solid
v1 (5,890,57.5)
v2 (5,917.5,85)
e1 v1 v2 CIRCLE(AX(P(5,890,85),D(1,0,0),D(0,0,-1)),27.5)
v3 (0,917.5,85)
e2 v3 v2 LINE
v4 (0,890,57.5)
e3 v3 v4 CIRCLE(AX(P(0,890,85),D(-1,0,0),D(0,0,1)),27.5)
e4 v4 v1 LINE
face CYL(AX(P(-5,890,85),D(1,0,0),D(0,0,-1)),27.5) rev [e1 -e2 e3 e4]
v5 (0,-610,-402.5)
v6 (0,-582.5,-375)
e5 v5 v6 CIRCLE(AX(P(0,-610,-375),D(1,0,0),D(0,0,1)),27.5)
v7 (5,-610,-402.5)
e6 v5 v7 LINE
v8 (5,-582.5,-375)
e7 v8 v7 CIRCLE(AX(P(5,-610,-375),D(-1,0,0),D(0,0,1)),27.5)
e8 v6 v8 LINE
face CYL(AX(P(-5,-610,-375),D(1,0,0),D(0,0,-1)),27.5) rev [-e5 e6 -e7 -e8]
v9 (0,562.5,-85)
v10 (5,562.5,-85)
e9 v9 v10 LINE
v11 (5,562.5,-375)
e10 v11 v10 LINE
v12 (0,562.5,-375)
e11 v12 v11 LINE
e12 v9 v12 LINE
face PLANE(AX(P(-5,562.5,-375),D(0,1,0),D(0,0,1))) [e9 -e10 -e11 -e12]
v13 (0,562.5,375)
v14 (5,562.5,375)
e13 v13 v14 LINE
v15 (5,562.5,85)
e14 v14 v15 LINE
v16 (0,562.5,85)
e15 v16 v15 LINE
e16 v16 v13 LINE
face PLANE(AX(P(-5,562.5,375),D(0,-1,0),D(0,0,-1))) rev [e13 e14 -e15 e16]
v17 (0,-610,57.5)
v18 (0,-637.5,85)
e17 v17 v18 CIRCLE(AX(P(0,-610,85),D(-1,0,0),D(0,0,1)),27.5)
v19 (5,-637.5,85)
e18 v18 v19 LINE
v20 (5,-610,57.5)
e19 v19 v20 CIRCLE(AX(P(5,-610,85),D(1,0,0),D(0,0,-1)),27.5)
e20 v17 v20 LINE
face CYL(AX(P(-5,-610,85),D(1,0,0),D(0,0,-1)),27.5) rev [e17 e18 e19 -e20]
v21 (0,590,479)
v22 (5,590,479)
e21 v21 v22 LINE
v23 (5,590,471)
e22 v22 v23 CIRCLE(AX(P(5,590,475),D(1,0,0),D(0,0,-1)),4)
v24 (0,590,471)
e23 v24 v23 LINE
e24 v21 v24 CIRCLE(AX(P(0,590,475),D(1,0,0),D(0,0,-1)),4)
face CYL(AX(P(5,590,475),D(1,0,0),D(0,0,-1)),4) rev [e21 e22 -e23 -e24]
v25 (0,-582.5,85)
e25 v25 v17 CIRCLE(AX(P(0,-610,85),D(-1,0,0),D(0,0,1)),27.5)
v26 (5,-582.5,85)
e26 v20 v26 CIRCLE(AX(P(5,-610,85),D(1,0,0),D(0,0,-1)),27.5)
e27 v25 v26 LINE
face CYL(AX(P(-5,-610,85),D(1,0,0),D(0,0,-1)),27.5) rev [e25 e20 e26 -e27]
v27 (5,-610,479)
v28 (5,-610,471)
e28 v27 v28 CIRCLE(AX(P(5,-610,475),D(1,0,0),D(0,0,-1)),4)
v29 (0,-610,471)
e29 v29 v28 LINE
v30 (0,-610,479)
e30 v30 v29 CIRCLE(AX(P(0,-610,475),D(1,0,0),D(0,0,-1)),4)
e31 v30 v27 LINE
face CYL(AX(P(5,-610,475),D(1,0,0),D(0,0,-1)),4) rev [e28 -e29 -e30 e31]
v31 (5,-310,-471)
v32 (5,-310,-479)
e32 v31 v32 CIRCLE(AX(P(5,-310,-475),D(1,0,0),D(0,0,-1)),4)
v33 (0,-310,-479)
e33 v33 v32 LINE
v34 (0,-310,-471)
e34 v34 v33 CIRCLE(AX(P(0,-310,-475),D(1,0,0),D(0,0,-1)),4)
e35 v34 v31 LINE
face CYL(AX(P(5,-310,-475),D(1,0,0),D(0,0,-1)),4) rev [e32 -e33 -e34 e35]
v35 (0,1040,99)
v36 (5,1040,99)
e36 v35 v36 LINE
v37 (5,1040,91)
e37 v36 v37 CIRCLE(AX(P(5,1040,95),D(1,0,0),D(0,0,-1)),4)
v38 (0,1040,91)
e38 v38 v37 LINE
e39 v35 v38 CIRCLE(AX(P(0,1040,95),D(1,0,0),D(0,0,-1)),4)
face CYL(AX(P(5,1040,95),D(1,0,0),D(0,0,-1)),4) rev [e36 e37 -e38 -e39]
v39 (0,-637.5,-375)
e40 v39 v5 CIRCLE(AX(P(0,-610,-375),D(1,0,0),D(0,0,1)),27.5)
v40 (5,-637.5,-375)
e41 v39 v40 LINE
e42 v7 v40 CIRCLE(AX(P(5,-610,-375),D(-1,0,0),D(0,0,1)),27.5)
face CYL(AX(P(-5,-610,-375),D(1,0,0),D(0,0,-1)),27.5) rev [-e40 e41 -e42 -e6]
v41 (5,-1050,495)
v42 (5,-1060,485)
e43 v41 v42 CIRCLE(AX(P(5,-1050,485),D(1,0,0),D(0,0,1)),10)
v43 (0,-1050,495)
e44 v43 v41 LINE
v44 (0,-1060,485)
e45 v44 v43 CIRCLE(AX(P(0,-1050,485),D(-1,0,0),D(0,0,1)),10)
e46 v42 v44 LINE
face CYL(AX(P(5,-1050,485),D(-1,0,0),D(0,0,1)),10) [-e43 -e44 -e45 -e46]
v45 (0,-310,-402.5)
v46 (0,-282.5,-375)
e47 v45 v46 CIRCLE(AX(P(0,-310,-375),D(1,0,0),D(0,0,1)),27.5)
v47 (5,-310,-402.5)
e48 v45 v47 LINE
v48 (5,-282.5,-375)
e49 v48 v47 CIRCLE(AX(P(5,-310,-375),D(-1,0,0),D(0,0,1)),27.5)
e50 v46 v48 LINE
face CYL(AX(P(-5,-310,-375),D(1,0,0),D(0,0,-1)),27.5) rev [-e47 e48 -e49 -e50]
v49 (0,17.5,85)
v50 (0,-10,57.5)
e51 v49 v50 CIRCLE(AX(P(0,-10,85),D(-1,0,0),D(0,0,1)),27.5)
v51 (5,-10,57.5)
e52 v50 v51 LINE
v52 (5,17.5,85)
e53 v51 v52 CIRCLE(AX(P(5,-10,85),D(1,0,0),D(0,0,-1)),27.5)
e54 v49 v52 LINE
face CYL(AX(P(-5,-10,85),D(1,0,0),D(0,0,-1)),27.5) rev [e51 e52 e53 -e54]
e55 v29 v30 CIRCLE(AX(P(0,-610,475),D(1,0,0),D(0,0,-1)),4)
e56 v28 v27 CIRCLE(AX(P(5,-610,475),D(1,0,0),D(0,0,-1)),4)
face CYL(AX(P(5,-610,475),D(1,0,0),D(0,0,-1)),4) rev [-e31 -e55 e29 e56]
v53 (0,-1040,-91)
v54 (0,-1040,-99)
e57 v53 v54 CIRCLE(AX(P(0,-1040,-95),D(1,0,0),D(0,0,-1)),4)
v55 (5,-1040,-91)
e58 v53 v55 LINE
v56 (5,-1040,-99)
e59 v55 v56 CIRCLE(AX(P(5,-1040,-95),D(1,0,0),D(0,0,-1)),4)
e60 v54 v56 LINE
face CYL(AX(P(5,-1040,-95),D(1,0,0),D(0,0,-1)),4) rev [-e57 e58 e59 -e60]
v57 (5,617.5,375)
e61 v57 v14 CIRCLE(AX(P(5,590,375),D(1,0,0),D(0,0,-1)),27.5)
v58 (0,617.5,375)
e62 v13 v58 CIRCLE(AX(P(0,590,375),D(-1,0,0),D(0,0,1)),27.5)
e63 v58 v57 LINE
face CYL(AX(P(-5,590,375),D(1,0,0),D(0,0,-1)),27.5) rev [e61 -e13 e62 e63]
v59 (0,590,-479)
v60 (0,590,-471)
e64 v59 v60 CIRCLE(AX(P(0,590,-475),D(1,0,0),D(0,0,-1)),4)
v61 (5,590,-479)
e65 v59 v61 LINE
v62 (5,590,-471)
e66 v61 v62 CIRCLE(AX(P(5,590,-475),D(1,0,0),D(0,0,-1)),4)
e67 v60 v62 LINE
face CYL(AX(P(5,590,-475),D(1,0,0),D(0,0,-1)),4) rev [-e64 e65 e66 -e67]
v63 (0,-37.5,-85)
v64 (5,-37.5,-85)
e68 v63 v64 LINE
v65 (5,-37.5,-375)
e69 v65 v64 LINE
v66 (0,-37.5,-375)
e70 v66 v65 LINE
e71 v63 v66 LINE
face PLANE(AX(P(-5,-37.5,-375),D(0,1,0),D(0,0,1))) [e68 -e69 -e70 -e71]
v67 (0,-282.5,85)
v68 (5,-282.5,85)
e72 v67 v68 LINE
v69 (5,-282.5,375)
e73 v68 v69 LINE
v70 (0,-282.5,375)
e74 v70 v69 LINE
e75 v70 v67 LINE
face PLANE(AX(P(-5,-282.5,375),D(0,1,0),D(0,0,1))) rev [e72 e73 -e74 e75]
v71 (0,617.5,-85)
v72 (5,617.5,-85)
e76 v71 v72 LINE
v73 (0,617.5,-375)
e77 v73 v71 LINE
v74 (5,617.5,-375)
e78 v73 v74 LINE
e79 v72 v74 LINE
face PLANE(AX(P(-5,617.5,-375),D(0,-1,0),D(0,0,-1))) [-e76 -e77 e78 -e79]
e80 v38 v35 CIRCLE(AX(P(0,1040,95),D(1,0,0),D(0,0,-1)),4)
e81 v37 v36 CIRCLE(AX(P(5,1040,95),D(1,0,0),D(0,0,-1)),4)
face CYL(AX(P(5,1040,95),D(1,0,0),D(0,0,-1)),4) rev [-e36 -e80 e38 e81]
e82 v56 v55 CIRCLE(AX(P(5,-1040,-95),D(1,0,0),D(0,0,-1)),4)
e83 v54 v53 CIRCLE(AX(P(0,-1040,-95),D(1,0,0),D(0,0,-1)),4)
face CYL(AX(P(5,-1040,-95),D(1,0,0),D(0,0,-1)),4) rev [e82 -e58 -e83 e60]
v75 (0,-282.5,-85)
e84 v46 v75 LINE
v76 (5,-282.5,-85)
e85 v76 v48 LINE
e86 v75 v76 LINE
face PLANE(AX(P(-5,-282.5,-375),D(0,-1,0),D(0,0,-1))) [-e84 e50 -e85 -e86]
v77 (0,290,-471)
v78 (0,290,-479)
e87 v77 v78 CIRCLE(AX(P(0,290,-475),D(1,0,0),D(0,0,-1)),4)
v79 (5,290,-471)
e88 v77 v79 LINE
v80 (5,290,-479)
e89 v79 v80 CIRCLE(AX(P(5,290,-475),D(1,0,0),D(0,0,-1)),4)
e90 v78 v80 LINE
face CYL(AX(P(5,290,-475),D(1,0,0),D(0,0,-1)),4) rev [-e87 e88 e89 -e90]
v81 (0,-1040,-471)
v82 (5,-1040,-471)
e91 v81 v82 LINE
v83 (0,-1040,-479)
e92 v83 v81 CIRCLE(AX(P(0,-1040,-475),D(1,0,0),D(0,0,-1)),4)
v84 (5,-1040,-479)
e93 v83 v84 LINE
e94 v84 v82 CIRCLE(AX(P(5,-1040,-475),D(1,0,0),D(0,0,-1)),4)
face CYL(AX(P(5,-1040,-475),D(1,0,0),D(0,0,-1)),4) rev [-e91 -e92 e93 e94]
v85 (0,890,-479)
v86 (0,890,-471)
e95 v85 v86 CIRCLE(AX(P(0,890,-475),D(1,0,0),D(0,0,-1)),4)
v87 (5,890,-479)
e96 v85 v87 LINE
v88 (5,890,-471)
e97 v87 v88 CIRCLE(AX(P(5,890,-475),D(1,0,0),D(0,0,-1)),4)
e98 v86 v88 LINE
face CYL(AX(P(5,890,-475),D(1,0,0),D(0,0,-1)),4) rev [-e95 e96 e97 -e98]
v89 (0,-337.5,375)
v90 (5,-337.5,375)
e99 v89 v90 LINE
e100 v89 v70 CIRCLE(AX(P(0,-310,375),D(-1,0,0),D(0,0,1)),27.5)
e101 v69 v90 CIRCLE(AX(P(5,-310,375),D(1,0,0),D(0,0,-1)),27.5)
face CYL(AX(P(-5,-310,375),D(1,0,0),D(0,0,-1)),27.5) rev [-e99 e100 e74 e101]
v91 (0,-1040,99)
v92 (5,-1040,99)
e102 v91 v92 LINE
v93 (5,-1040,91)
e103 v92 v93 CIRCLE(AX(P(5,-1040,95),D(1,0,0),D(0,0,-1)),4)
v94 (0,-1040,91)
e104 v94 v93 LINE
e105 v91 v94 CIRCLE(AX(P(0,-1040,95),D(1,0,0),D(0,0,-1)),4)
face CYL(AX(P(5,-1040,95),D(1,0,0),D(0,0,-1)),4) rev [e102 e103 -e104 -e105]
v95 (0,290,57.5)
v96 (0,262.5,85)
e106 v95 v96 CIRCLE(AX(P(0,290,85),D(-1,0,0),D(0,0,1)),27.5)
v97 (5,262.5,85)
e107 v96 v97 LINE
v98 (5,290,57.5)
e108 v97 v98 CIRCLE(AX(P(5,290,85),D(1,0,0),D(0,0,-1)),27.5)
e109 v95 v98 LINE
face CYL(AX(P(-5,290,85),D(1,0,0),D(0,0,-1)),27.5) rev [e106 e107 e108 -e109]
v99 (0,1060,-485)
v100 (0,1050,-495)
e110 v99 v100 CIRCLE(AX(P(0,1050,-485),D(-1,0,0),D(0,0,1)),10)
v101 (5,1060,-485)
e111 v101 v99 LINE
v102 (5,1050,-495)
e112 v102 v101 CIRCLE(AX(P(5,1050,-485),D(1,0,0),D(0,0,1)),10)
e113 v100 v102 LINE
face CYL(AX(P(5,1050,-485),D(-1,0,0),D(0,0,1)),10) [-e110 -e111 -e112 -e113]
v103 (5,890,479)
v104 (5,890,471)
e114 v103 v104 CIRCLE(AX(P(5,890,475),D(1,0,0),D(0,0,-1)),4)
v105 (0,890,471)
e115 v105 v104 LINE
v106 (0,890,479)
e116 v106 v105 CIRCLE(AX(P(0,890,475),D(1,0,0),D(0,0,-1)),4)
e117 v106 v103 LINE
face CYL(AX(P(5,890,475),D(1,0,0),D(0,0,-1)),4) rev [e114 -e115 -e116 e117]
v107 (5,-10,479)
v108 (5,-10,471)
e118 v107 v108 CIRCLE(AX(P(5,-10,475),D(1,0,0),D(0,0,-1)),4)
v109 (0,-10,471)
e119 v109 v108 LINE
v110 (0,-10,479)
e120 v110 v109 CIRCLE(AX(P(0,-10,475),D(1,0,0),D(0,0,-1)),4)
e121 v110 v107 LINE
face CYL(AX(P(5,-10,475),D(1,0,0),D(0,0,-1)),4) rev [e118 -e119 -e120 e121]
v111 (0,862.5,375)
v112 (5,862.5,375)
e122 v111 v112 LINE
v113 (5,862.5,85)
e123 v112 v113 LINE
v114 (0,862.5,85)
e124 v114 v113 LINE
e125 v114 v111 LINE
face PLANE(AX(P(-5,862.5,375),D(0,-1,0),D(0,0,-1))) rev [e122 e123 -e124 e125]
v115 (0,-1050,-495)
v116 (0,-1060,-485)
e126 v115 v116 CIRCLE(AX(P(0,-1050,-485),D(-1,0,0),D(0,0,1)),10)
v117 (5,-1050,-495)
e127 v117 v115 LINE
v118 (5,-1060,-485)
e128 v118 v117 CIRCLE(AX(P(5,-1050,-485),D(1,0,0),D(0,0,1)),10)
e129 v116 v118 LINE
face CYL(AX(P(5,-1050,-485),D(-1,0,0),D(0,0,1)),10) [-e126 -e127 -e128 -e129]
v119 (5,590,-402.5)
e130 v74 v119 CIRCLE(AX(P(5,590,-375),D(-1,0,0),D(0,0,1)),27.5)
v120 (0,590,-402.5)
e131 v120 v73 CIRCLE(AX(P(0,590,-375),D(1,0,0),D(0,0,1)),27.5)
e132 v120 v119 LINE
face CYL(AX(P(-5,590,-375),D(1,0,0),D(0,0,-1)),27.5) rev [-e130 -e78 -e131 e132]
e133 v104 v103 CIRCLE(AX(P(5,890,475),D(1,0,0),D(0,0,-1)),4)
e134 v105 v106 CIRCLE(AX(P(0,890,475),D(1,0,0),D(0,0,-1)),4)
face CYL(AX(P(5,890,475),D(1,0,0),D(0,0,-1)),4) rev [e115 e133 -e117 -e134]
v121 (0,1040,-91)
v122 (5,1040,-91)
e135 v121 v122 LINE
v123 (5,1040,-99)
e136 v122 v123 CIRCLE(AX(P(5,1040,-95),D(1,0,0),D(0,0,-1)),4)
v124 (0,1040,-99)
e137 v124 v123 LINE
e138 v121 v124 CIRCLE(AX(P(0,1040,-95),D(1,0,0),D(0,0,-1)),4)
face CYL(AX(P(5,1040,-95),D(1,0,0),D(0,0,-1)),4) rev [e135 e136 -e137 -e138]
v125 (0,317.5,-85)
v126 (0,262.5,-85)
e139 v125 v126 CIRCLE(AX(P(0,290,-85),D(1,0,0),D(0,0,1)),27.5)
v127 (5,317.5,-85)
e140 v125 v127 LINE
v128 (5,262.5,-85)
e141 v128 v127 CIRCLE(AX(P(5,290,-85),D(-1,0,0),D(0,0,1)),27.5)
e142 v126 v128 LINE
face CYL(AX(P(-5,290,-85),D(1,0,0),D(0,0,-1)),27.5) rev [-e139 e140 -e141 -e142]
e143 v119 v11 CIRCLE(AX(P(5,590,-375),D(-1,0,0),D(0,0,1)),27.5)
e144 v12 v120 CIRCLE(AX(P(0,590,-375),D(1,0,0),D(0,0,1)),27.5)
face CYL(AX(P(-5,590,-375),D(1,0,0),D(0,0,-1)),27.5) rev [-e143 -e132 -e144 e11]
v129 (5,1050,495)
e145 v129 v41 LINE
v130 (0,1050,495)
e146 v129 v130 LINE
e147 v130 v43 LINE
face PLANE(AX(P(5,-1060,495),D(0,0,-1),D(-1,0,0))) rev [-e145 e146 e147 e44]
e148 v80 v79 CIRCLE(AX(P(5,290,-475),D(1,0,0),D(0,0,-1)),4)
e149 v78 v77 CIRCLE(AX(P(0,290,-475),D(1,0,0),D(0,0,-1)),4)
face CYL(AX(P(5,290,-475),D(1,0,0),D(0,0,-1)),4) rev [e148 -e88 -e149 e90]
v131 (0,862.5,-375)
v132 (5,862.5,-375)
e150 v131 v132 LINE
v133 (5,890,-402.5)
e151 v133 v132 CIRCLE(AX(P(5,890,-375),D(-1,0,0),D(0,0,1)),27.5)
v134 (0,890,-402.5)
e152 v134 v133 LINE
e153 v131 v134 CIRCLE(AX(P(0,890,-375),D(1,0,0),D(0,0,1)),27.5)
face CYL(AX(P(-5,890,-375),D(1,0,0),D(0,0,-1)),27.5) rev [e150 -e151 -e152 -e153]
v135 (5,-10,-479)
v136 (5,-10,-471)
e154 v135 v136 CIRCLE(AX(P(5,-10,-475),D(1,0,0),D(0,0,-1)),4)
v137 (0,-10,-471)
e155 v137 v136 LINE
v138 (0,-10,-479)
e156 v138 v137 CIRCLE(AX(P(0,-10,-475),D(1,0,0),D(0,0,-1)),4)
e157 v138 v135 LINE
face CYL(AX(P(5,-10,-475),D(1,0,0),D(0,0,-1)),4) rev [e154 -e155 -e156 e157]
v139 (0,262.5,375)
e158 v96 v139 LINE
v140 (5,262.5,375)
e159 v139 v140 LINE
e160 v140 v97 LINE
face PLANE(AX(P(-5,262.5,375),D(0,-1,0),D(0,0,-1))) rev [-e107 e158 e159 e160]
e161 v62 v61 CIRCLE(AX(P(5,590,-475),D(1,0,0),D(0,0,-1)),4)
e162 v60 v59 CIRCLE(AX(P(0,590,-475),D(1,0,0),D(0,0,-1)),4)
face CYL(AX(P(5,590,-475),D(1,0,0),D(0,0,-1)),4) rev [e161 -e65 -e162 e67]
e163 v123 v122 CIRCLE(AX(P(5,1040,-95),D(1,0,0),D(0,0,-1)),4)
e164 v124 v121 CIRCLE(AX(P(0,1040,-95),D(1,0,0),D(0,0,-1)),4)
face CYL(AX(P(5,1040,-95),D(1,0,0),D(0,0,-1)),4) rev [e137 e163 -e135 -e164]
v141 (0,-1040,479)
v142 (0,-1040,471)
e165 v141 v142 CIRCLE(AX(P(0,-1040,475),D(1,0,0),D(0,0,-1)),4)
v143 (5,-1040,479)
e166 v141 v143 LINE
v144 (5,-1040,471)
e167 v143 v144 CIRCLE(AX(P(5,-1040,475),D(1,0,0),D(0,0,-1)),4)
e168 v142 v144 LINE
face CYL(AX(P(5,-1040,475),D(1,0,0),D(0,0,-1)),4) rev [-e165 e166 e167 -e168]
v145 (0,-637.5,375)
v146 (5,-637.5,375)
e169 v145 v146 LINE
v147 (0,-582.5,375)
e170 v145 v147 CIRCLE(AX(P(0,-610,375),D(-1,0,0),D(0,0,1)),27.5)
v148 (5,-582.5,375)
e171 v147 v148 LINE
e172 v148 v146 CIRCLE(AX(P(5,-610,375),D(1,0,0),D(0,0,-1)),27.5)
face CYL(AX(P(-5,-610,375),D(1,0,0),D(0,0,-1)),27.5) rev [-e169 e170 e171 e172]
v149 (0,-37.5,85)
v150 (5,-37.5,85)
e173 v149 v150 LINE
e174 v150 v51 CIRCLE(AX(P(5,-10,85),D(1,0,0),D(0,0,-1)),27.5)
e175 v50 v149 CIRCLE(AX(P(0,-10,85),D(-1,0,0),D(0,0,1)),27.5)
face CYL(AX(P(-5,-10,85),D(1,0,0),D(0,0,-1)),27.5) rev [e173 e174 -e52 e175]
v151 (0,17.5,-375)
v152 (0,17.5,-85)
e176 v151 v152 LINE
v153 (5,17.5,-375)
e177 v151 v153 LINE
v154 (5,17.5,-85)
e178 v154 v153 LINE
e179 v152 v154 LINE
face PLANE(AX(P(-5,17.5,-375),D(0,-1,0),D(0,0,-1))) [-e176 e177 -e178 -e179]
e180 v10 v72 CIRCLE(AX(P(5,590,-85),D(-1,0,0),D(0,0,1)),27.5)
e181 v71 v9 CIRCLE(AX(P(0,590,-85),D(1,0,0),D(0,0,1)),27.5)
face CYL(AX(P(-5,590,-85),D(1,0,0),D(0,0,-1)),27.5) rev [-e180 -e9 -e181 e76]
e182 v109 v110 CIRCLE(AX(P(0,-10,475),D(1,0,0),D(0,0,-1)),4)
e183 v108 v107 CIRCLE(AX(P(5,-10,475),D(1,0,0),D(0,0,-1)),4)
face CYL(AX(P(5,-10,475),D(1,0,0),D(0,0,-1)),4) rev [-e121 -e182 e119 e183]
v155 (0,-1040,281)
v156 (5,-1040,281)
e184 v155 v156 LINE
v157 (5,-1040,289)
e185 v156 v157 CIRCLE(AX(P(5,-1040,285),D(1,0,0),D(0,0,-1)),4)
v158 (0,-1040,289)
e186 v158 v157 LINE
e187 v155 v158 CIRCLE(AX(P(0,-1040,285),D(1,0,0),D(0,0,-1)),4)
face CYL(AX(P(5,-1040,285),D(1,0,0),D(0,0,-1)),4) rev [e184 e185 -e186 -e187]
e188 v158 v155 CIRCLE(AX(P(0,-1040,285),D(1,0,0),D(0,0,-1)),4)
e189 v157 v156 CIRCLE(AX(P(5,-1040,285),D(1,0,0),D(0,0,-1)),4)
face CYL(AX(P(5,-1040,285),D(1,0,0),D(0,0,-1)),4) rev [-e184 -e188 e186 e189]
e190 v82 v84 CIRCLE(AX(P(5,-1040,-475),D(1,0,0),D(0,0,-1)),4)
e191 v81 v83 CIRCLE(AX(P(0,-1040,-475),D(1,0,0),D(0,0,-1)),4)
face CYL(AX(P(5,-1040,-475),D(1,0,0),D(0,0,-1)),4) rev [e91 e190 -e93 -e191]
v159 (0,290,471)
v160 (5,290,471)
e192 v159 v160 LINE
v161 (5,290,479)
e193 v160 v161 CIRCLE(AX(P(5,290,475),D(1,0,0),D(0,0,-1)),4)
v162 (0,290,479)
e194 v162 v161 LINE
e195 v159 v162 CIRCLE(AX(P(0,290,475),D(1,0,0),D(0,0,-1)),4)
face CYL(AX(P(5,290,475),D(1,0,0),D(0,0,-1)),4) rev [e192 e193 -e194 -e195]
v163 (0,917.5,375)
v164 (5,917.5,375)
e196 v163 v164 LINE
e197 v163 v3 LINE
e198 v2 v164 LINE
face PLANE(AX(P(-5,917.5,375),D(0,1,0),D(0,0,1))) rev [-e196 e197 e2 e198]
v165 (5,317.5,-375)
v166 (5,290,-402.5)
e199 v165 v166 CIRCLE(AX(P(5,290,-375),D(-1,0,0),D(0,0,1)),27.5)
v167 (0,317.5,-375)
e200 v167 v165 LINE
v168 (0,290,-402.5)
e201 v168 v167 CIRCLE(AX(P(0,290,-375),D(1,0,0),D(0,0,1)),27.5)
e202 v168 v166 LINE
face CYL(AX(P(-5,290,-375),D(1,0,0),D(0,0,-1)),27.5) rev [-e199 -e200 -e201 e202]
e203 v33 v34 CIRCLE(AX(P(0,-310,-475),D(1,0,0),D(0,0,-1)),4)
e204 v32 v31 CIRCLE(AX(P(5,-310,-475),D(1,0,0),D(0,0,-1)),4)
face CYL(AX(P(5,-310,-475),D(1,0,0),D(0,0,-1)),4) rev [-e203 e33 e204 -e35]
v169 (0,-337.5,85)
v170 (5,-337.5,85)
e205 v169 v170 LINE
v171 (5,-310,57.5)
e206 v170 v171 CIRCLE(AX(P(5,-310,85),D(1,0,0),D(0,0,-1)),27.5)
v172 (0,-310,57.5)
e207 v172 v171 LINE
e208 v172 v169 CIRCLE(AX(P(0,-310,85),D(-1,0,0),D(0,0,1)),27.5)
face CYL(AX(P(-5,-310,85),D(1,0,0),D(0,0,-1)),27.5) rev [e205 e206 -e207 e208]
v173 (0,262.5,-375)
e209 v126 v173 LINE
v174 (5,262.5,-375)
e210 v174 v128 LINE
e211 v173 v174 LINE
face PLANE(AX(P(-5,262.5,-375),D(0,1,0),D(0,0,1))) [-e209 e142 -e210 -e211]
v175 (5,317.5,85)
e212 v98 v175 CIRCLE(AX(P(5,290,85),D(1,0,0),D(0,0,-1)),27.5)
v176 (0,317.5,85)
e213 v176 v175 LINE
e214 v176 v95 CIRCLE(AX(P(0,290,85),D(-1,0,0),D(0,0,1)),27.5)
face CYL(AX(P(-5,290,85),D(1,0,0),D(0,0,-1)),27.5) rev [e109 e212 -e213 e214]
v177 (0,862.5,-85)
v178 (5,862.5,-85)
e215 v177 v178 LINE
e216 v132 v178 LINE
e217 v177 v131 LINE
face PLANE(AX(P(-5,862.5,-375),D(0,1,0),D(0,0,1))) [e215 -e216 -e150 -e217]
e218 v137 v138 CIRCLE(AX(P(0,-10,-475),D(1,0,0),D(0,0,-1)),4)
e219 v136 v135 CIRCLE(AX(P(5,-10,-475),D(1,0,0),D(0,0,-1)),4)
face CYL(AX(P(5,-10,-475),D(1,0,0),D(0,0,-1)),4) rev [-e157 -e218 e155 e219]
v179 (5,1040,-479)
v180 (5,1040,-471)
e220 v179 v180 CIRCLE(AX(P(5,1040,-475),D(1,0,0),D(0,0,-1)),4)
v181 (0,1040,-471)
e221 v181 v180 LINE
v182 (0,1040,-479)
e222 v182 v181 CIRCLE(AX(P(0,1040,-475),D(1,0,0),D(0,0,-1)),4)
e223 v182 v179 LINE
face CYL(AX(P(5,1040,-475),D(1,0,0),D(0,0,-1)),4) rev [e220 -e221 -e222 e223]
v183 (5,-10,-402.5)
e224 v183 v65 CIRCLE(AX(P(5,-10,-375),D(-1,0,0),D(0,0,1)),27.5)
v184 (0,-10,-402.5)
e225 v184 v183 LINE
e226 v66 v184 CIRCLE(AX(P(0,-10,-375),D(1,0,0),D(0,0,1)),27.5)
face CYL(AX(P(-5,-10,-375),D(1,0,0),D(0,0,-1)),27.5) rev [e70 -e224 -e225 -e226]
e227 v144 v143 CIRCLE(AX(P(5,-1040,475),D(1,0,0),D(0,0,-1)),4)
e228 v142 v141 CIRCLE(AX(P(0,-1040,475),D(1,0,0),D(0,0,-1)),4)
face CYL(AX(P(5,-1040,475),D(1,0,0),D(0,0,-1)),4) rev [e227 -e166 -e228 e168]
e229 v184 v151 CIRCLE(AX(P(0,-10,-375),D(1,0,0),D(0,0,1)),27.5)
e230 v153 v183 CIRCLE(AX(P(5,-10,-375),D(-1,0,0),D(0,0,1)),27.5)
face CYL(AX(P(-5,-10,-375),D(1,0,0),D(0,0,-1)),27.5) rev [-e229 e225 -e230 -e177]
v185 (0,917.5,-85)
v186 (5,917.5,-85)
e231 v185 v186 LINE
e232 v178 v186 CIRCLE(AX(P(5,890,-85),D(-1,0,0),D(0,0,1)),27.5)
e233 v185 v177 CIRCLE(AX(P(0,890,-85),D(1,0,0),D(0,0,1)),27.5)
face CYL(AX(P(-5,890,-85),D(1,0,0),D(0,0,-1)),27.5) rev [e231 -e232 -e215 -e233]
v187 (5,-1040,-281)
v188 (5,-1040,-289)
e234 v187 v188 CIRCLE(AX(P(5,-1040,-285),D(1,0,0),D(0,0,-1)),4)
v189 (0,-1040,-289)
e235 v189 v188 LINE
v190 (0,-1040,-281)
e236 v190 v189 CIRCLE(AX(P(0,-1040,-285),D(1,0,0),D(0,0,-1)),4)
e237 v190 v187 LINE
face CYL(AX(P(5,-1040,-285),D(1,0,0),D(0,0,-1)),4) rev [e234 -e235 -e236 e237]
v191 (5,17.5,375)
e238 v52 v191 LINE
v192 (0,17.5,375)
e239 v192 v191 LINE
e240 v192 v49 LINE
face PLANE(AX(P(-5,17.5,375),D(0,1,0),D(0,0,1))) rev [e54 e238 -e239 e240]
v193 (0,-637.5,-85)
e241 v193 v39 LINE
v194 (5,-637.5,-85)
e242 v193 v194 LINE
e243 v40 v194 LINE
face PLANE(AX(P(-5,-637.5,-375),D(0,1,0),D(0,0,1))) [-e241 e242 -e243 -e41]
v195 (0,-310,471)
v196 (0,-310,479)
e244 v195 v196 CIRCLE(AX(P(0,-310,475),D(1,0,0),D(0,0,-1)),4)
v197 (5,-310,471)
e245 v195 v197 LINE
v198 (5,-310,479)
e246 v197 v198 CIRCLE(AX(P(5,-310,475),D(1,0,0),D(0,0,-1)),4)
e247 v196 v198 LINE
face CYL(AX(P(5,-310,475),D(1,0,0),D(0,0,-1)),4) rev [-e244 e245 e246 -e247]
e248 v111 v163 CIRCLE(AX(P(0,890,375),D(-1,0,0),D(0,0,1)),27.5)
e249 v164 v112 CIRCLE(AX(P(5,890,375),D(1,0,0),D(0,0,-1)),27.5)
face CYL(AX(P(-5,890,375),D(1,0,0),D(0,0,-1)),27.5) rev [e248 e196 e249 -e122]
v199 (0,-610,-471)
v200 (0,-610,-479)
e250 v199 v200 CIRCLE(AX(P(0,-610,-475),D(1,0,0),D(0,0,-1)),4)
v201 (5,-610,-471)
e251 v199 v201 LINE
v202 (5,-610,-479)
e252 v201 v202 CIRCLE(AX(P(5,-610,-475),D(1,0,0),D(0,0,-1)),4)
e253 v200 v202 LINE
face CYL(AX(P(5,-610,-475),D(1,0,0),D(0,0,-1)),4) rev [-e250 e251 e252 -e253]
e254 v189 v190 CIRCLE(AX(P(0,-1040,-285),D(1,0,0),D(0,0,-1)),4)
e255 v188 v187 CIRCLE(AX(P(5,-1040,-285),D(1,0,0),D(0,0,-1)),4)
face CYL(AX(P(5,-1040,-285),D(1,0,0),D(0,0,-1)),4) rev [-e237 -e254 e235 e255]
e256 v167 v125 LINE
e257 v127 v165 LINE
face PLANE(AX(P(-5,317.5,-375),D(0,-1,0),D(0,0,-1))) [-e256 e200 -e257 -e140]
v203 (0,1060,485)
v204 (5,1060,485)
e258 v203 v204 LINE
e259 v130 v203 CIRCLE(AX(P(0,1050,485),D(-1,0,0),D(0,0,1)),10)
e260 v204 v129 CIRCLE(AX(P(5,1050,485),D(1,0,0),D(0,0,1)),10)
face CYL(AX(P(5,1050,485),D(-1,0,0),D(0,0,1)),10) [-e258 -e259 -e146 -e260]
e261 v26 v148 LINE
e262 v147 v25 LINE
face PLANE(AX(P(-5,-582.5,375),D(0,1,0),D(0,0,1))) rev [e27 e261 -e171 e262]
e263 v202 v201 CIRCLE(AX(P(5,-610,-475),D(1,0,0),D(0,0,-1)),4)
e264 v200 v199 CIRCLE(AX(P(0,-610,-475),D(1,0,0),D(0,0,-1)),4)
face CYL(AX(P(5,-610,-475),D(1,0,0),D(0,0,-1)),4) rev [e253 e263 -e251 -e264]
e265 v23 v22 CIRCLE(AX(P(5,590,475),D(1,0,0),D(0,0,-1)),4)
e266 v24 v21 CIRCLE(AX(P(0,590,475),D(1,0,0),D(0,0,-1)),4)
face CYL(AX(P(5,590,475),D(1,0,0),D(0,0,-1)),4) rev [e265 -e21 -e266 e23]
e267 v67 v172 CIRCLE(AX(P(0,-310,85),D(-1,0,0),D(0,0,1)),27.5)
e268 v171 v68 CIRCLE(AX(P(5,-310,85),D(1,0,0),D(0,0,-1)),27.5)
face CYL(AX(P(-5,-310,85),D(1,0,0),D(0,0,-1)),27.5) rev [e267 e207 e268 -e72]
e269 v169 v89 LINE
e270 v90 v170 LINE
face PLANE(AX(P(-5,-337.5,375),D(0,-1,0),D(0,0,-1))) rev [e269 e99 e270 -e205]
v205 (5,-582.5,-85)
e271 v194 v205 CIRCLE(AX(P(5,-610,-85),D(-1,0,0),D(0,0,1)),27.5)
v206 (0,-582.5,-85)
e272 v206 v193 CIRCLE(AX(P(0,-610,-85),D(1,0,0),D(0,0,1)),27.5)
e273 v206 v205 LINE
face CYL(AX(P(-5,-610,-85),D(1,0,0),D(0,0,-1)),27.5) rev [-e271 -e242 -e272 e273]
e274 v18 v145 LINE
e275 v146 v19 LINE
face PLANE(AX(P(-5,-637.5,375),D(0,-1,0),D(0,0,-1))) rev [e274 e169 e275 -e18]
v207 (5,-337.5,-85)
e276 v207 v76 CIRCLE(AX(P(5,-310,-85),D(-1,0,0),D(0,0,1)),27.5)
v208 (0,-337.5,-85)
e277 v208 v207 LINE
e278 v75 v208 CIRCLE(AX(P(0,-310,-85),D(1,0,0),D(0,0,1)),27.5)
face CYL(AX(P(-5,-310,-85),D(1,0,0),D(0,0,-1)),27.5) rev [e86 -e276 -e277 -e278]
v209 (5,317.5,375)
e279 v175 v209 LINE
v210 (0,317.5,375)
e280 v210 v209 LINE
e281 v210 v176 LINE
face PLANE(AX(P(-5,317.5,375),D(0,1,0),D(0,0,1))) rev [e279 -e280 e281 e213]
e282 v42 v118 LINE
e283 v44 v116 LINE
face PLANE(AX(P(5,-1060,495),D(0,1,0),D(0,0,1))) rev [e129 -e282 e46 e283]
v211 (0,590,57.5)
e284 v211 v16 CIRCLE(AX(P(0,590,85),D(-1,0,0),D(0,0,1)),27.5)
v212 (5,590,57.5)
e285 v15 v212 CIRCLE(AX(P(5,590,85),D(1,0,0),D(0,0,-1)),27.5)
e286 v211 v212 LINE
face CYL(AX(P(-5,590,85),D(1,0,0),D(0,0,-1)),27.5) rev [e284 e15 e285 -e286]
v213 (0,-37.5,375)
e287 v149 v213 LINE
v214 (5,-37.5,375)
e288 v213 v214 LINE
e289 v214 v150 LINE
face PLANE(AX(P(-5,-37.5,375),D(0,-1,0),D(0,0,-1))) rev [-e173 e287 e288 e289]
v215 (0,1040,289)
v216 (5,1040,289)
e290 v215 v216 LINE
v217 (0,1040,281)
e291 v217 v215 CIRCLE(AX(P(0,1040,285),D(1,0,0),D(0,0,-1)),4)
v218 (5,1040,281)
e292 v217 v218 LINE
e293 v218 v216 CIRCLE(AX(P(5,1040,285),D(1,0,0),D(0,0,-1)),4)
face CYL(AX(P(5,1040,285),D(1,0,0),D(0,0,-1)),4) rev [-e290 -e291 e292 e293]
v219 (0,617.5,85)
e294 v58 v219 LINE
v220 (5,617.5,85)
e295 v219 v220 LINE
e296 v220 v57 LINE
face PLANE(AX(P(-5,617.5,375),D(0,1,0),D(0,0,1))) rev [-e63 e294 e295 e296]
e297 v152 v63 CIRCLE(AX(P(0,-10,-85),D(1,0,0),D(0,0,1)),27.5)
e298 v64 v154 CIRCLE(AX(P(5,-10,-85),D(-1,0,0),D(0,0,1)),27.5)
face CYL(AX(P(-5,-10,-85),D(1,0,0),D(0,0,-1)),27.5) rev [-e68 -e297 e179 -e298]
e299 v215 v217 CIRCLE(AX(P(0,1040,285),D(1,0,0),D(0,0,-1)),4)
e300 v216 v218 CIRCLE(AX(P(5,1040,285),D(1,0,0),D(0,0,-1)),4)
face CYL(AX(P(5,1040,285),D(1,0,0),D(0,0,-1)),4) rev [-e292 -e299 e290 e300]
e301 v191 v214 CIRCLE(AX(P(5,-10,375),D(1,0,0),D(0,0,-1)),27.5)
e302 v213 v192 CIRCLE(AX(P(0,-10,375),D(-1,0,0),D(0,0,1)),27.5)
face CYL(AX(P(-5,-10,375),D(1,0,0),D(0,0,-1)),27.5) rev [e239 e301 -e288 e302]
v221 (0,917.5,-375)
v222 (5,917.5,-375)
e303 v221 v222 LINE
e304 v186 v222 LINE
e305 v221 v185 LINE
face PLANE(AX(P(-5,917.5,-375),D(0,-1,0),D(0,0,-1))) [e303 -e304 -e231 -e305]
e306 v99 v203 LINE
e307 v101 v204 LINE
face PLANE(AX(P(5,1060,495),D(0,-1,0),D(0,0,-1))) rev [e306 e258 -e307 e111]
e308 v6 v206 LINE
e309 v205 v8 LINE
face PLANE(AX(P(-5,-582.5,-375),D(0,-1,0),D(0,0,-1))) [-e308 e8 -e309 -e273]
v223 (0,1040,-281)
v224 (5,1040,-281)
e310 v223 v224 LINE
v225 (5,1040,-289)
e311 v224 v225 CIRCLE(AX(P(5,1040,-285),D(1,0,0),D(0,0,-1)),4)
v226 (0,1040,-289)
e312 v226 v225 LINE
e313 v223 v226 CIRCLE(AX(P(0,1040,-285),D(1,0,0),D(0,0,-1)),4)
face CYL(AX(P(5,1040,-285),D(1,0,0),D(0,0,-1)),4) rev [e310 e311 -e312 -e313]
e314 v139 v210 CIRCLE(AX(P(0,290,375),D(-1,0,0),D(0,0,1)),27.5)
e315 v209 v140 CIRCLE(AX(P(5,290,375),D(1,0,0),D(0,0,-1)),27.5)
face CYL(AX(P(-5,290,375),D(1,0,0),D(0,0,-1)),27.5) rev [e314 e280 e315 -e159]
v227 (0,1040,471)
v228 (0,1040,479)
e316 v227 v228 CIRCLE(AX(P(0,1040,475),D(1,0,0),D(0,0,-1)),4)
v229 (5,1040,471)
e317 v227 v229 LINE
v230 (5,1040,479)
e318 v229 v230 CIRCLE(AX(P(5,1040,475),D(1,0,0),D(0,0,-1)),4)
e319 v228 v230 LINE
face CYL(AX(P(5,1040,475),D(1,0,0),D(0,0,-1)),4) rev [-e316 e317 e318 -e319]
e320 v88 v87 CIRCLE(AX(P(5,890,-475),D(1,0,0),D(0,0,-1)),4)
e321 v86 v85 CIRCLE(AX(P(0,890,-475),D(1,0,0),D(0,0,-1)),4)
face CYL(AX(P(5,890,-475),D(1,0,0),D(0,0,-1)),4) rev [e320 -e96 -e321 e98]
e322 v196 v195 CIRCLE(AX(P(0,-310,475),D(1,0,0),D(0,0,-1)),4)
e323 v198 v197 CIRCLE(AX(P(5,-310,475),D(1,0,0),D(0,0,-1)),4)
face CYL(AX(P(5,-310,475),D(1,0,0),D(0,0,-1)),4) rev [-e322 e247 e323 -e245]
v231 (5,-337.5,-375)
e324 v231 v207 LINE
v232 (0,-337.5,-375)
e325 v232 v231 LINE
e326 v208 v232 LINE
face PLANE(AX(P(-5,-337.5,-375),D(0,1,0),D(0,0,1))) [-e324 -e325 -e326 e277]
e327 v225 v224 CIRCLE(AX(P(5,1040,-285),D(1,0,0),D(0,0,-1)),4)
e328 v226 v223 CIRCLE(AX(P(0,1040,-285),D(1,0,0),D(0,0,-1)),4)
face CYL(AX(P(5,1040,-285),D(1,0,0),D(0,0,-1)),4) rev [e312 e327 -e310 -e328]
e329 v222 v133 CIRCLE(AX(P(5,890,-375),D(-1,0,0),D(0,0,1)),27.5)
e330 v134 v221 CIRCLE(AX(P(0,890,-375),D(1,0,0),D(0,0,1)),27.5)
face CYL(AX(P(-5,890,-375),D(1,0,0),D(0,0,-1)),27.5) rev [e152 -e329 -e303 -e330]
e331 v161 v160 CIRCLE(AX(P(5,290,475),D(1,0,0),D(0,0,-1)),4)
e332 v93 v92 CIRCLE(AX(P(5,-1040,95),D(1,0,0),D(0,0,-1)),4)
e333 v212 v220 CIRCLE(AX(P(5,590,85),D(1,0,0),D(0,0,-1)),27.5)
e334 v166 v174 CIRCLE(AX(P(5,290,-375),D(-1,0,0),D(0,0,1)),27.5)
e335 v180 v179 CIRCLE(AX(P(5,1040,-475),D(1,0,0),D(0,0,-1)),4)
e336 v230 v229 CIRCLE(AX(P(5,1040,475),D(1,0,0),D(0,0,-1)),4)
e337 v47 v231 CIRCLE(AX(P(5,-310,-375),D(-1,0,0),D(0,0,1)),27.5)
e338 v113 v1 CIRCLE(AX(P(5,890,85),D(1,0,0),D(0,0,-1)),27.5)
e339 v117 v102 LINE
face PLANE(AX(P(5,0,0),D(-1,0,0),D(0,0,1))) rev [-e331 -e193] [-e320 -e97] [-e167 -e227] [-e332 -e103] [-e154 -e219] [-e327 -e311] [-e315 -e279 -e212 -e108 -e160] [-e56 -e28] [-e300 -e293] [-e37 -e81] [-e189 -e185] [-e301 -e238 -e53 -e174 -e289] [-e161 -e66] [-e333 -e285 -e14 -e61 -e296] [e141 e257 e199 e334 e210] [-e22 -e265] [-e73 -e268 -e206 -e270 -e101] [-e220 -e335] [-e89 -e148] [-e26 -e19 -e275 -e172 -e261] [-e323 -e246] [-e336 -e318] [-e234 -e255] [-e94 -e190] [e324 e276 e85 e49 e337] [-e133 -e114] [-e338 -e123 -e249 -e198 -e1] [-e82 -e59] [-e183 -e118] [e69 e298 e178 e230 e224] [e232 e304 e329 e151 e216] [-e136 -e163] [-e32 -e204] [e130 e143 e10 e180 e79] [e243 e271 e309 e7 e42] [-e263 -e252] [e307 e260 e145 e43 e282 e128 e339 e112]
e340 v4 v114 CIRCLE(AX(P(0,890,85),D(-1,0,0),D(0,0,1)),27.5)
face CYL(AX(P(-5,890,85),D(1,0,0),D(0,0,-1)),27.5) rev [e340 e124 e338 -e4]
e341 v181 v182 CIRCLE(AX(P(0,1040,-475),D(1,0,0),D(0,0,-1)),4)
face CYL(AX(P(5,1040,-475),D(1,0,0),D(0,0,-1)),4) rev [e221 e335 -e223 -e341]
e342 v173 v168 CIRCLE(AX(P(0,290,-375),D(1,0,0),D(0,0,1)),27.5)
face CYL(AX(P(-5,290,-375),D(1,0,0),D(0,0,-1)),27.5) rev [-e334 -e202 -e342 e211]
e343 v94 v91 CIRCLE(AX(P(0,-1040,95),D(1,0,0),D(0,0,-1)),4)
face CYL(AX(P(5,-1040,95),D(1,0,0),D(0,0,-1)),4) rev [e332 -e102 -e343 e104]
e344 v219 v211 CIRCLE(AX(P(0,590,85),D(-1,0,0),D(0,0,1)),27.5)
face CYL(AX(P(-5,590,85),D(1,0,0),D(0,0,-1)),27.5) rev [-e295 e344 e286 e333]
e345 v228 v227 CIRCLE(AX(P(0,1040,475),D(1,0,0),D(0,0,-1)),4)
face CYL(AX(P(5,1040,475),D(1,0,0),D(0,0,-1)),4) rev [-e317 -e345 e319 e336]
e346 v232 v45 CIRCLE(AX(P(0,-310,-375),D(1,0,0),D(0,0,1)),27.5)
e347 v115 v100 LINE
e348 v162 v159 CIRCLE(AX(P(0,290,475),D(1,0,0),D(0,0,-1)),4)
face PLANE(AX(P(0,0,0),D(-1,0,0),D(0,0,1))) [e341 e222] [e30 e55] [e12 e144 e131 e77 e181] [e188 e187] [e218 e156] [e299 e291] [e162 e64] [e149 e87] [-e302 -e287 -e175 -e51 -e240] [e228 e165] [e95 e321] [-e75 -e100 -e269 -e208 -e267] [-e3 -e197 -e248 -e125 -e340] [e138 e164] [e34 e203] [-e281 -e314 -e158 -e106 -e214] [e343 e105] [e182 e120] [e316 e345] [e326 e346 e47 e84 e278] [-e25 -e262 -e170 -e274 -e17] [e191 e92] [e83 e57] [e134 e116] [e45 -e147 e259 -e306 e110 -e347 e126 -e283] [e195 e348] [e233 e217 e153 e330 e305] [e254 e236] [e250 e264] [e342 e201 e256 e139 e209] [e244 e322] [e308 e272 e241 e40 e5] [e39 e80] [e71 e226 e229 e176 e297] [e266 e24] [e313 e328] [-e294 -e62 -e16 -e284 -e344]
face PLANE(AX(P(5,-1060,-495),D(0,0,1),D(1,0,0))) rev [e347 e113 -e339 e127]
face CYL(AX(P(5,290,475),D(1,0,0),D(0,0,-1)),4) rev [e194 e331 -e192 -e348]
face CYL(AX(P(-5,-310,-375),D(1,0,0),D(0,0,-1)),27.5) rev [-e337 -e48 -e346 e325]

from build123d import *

# Parameters (mm, degrees)
SKETCH1_W                     = 990
SKETCH1_H                     = 2120
BOSS_EXTRUDE1_DEPTH           = 5
FILLET1_R                     = 10
M7_CLEARANCE_HOLE3_D          = 8
M7_CLEARANCE_HOLE2_AT_2_COUNT = 2
M7_CLEARANCE_HOLE2_AT_2_PITCH = 950
LPATTERN7_COUNT               = 6
LPATTERN7_PITCH               = 300
CUT_EXTRUDE5_DEPTH            = 10
LPATTERN8_COUNT               = 6
LPATTERN8_PITCH               = 300
MIRROR6_COPY_1_DEPTH          = 10
MIRROR6_COPY_2_DEPTH          = 10
MIRROR6_COPY_3_DEPTH          = 10
MIRROR6_COPY_4_DEPTH          = 10
MIRROR6_COPY_5_DEPTH          = 10


with BuildPart() as part:
    # Sketch1 → Boss-Extrude1 (new body)
    with BuildSketch(Plane(origin=(0, 0, 0), x_dir=(0, 0, -1), z_dir=(1, 0, 0))):
        Rectangle(SKETCH1_W, SKETCH1_H)
    extrude(amount=BOSS_EXTRUDE1_DEPTH)

    # Fillet1
    fillet1_edges = [part.edges().sort_by_distance(p)[0] for p in [
        (2.5, -1060, -495),
        (2.5, -1060, 495),
        (2.5, 1060, 495),
        (2.5, 1060, -495),
    ]]
    fillet(fillet1_edges, radius=FILLET1_R)

    # M7 Clearance Hole3 (through all)
    with Locations(Plane(origin=(5, 0, 0), x_dir=(0, 0, -1), z_dir=(1, 0, 0))):
        with Locations((-475, 1040), (-285, 1040), (-95, 1040), (95, 1040), (285, 1040), (475, 1040)):
            m7_clearance_hole3 = Hole(M7_CLEARANCE_HOLE3_D / 2)

    # Mirror5: M7 Clearance Hole3 across plane
    add(m7_clearance_hole3.mirror(Plane(origin=(0, 0, 0), x_dir=(0, 0, 1), z_dir=(0, -1, 0))), mode=Mode.SUBTRACT)

    # Sketch15 → M7 Clearance Hole2 (revolve, cut)
    with BuildSketch(Plane(origin=(5, 890, 475), x_dir=(0, 0, -1), z_dir=(0, 1, 0))):
        Polygon((0, 0), (0, 7.403442476), (4, 5), (4, 0), align=None)
    m7_clearance_hole2 = revolve(axis=Axis((11.35, 890, 475), (-1, 0, 0)), mode=Mode.SUBTRACT)

    # M7 Clearance Hole2 at 2: M7 Clearance Hole2 ×2
    with Locations(*[(0, 0, -i * M7_CLEARANCE_HOLE2_AT_2_PITCH) for i in range(1, M7_CLEARANCE_HOLE2_AT_2_COUNT)]):
        add(m7_clearance_hole2, mode=Mode.SUBTRACT)

    # LPattern7: M7 Clearance Hole2 ×6
    with Locations(*[(0, -i * LPATTERN7_PITCH, 0) for i in range(1, LPATTERN7_COUNT)]):
        add(m7_clearance_hole2, mode=Mode.SUBTRACT)

    # LPattern7 copy 1 sketch → LPattern7 copy 1 (revolve, cut)
    with BuildSketch(Plane(origin=(5, 590, -475), x_dir=(0, 0, -1), z_dir=(0, 1, 0))):
        Polygon((0, 0), (0, 7.403442476), (4, 5), (4, 0), align=None)
    revolve(axis=Axis((11.35, 590, -475), (-1, 0, 0)), mode=Mode.SUBTRACT)

    # LPattern7 copy 2 sketch → LPattern7 copy 2 (revolve, cut)
    with BuildSketch(Plane(origin=(5, 290, -475), x_dir=(0, 0, -1), z_dir=(0, 1, 0))):
        Polygon((0, 0), (0, 7.403442476), (4, 5), (4, 0), align=None)
    revolve(axis=Axis((11.35, 290, -475), (-1, 0, 0)), mode=Mode.SUBTRACT)

    # LPattern7 copy 3 sketch → LPattern7 copy 3 (revolve, cut)
    with BuildSketch(Plane(origin=(5, -10, -475), x_dir=(0, 0, -1), z_dir=(0, 1, 0))):
        Polygon((0, 0), (0, 7.403442476), (4, 5), (4, 0), align=None)
    revolve(axis=Axis((11.35, -10, -475), (-1, 0, 0)), mode=Mode.SUBTRACT)

    # LPattern7 copy 4 sketch → LPattern7 copy 4 (revolve, cut)
    with BuildSketch(Plane(origin=(5, -310, -475), x_dir=(0, 0, -1), z_dir=(0, 1, 0))):
        Polygon((0, 0), (0, 7.403442476), (4, 5), (4, 0), align=None)
    revolve(axis=Axis((11.35, -310, -475), (-1, 0, 0)), mode=Mode.SUBTRACT)

    # LPattern7 copy 5 sketch → LPattern7 copy 5 (revolve, cut)
    with BuildSketch(Plane(origin=(5, -610, -475), x_dir=(0, 0, -1), z_dir=(0, 1, 0))):
        Polygon((0, 0), (0, 7.403442476), (4, 5), (4, 0), align=None)
    revolve(axis=Axis((11.35, -610, -475), (-1, 0, 0)), mode=Mode.SUBTRACT)

    # Sketch18 → Cut-Extrude5 (cut)
    with BuildSketch(Plane(origin=(5, 0, 0), x_dir=(0, 0, -1), z_dir=(1, 0, 0))):
        with BuildLine():
            Line((-375, 917.5), (-85, 917.5))
            ThreePointArc((-85, 917.5), (-57.5, 890), (-85, 862.5))
            Line((-85, 862.5), (-375, 862.5))
            ThreePointArc((-375, 862.5), (-402.5, 890), (-375, 917.5))
        make_face()
    cut_extrude5 = extrude(amount=-CUT_EXTRUDE5_DEPTH, mode=Mode.SUBTRACT)

    # LPattern8: Cut-Extrude5 ×6
    with Locations(*[(0, -i * LPATTERN8_PITCH, 0) for i in range(1, LPATTERN8_COUNT)]):
        add(cut_extrude5, mode=Mode.SUBTRACT)

    # Mirror6: Cut-Extrude5 across plane
    add(cut_extrude5.mirror(Plane.XY), mode=Mode.SUBTRACT)

    # Mirror6 copy 1 sketch → Mirror6 copy 1 (cut)
    with BuildSketch(Plane(origin=(5, -300, 0), x_dir=(0, 0, 1), z_dir=(1, 0, 0))):
        with BuildLine():
            Line((-375, -917.5), (-85, -917.5))
            ThreePointArc((-85, -917.5), (-57.5, -890), (-85, -862.5))
            Line((-85, -862.5), (-375, -862.5))
            ThreePointArc((-375, -862.5), (-402.5, -890), (-375, -917.5))
        make_face()
    extrude(amount=-MIRROR6_COPY_1_DEPTH, mode=Mode.SUBTRACT)

    # Mirror6 copy 2 sketch → Mirror6 copy 2 (cut)
    with BuildSketch(Plane(origin=(5, -600, 0), x_dir=(0, 0, 1), z_dir=(1, 0, 0))):
        with BuildLine():
            Line((-375, -917.5), (-85, -917.5))
            ThreePointArc((-85, -917.5), (-57.5, -890), (-85, -862.5))
            Line((-85, -862.5), (-375, -862.5))
            ThreePointArc((-375, -862.5), (-402.5, -890), (-375, -917.5))
        make_face()
    extrude(amount=-MIRROR6_COPY_2_DEPTH, mode=Mode.SUBTRACT)

    # Mirror6 copy 3 sketch → Mirror6 copy 3 (cut)
    with BuildSketch(Plane(origin=(5, -900, 0), x_dir=(0, 0, 1), z_dir=(1, 0, 0))):
        with BuildLine():
            Line((-375, -917.5), (-85, -917.5))
            ThreePointArc((-85, -917.5), (-57.5, -890), (-85, -862.5))
            Line((-85, -862.5), (-375, -862.5))
            ThreePointArc((-375, -862.5), (-402.5, -890), (-375, -917.5))
        make_face()
    extrude(amount=-MIRROR6_COPY_3_DEPTH, mode=Mode.SUBTRACT)

    # Mirror6 copy 4 sketch → Mirror6 copy 4 (cut)
    with BuildSketch(Plane(origin=(5, -1200, 0), x_dir=(0, 0, 1), z_dir=(1, 0, 0))):
        with BuildLine():
            Line((-375, -917.5), (-85, -917.5))
            ThreePointArc((-85, -917.5), (-57.5, -890), (-85, -862.5))
            Line((-85, -862.5), (-375, -862.5))
            ThreePointArc((-375, -862.5), (-402.5, -890), (-375, -917.5))
        make_face()
    extrude(amount=-MIRROR6_COPY_4_DEPTH, mode=Mode.SUBTRACT)

    # Mirror6 copy 5 sketch → Mirror6 copy 5 (cut)
    with BuildSketch(Plane(origin=(5, -1500, 0), x_dir=(0, 0, 1), z_dir=(1, 0, 0))):
        with BuildLine():
            Line((-375, -917.5), (-85, -917.5))
            ThreePointArc((-85, -917.5), (-57.5, -890), (-85, -862.5))
            Line((-85, -862.5), (-375, -862.5))
            ThreePointArc((-375, -862.5), (-402.5, -890), (-375, -917.5))
        make_face()
    extrude(amount=-MIRROR6_COPY_5_DEPTH, mode=Mode.SUBTRACT)


solid = part.part
